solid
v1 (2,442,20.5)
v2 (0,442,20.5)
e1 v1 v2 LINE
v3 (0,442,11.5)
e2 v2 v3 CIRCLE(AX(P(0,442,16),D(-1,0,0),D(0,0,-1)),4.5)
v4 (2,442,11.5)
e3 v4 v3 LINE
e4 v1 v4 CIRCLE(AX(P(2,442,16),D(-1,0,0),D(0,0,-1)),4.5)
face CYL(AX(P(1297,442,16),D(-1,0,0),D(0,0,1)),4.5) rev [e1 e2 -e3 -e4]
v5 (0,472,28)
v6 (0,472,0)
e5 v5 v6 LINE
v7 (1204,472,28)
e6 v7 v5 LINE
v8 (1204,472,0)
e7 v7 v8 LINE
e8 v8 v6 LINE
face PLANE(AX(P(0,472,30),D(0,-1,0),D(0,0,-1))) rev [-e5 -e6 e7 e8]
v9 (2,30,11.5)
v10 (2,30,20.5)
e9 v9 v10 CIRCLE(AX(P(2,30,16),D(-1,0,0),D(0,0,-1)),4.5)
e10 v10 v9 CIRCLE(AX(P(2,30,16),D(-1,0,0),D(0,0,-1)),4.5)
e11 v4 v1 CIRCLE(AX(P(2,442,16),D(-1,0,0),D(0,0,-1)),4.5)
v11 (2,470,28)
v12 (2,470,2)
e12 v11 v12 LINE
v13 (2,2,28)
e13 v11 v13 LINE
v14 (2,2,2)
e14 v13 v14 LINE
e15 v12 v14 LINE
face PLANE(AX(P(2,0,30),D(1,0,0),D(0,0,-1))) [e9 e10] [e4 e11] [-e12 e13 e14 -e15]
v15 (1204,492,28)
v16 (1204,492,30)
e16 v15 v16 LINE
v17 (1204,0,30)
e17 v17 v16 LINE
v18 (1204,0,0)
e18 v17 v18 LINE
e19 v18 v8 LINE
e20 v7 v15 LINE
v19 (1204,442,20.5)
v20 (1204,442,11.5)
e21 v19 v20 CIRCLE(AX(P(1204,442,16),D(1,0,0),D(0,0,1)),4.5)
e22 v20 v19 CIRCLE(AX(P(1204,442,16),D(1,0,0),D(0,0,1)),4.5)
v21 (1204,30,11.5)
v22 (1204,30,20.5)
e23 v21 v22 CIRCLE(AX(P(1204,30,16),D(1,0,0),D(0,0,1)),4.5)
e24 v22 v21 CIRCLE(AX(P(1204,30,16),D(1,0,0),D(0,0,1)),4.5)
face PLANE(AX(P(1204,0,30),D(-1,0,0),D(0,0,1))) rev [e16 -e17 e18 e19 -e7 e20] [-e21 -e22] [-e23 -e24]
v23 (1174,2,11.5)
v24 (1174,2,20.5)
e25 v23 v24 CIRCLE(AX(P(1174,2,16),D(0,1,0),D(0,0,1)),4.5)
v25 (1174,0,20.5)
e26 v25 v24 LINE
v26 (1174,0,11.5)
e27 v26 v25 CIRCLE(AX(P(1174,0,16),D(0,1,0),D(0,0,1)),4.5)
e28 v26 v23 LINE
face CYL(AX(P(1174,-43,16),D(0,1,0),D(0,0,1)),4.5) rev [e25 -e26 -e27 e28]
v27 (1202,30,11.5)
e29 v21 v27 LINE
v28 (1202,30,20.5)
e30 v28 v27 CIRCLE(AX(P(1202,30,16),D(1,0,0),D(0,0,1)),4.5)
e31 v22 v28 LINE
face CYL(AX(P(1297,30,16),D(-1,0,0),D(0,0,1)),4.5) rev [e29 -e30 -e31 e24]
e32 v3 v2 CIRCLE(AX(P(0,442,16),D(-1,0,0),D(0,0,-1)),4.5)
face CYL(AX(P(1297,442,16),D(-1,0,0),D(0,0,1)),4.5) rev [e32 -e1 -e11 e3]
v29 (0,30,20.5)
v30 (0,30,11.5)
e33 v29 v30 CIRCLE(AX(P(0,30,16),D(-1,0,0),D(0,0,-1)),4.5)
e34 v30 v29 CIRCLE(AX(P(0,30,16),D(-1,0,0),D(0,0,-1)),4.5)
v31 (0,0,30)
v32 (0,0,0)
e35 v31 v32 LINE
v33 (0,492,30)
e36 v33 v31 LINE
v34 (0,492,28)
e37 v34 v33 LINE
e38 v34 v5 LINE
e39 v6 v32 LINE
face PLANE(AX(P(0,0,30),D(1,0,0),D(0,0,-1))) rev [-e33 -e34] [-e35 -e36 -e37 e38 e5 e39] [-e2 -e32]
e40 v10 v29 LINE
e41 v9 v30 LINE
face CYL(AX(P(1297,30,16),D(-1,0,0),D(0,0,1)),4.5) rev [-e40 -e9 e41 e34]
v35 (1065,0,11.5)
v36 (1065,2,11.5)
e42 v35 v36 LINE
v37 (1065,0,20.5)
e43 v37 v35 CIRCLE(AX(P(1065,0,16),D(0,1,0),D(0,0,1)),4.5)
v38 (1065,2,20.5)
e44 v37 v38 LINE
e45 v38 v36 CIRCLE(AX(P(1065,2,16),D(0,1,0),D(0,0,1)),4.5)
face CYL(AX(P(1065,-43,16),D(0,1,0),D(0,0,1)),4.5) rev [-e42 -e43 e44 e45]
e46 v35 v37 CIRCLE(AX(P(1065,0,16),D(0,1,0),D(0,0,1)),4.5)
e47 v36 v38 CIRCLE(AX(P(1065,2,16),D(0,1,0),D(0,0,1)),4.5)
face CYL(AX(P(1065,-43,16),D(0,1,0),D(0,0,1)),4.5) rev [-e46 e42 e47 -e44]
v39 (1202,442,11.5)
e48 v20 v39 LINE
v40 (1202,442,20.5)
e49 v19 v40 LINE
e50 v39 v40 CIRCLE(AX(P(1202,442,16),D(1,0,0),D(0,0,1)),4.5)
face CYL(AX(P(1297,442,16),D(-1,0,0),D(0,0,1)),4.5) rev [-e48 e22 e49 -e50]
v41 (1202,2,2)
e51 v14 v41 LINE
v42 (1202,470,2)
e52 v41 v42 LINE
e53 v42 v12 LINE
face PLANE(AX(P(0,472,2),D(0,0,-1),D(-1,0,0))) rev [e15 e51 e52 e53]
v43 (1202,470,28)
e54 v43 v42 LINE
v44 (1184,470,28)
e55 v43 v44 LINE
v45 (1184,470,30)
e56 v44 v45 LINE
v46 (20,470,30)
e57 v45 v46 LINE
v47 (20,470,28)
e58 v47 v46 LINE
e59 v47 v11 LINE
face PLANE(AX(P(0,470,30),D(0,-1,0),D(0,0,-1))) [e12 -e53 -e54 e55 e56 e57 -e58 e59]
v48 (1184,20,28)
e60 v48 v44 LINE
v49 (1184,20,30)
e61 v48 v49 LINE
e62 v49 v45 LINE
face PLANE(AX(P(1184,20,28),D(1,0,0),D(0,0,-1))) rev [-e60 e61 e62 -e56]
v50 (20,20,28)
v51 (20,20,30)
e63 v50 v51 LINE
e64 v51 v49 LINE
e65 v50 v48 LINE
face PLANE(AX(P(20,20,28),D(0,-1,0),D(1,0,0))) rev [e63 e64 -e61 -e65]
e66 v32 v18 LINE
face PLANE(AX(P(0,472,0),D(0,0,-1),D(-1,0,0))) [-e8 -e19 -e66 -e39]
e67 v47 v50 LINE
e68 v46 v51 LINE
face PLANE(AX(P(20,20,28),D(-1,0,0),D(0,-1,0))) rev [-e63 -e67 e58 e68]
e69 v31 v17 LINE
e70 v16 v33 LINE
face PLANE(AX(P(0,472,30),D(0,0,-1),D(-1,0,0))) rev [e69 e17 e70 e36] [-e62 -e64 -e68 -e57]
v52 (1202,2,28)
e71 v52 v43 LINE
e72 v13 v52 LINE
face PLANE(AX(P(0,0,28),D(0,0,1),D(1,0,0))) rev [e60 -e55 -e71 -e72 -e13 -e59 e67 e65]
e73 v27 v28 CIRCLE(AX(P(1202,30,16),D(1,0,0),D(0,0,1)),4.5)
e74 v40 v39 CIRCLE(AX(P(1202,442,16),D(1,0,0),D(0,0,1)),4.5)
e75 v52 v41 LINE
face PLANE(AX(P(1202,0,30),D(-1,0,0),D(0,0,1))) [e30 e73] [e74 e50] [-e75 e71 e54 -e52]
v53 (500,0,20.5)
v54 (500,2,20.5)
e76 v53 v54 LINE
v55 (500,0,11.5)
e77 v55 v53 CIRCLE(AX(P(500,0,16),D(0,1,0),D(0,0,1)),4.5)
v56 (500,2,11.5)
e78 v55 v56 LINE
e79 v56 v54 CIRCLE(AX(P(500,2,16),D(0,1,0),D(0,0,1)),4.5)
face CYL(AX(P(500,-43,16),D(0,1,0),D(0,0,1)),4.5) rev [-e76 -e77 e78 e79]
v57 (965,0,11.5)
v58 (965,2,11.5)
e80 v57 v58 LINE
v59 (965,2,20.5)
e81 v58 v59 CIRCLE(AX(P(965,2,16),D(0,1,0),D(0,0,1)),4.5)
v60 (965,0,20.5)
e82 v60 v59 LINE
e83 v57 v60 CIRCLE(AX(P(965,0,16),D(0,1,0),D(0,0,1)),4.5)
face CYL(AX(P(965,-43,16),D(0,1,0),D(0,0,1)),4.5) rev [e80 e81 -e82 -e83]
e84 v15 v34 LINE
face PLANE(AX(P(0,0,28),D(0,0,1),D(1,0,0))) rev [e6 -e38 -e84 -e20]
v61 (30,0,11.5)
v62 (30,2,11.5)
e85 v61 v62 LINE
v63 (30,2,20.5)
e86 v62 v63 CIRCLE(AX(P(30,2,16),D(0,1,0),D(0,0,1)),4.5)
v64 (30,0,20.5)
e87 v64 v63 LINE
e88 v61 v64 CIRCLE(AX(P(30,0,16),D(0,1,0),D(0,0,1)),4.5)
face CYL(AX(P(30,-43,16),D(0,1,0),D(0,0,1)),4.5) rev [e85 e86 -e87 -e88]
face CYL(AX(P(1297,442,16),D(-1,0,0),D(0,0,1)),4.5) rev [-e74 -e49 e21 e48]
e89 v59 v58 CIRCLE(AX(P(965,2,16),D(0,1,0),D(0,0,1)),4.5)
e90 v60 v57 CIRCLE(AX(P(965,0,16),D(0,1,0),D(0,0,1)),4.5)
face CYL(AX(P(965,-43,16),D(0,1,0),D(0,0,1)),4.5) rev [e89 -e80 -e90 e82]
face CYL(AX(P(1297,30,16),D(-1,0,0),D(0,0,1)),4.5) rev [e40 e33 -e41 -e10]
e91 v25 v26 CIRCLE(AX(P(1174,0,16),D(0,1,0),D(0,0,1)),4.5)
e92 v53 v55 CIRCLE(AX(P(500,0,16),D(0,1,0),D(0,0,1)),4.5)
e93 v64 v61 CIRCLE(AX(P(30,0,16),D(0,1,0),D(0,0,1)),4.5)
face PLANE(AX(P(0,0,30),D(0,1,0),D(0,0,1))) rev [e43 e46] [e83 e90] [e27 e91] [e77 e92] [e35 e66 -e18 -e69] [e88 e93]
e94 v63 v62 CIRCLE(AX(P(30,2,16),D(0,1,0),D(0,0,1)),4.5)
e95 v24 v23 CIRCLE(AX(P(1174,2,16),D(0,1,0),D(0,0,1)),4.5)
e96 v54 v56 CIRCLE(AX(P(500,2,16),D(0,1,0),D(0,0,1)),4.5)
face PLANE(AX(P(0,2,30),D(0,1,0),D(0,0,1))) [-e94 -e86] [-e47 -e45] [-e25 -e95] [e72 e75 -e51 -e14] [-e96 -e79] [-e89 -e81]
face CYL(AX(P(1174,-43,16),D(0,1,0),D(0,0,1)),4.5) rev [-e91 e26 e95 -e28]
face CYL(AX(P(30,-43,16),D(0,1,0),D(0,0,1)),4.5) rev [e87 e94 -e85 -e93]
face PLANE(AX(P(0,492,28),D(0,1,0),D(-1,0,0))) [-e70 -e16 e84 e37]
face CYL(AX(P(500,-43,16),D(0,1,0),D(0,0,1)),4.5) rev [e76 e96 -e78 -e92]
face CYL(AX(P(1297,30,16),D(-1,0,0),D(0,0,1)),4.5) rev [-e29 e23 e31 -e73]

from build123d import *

# Parameters (mm, degrees)
SKETCH_1_W               = 1204
SKETCH_1_H               = 472
EXTRUDE_1_DEPTH          = 30
SHELL_1_T                = -2
SKETCH_2_W               = 1204
SKETCH_2_H               = 492
SKETCH_2_W_2             = 1164
SKETCH_2_H_2             = 450
EXTRUDE_2_DEPTH          = 2
CUT_EXTRUDE_1_DEPTH      = 1295
CUT_EXTRUDE_1_DEPTH_BACK = 72
SKETCH_3_R               = 4.5
SKETCH_4_R               = 4.5
CUT_EXTRUDE_2_DEPTH      = 45


with BuildPart() as part:
    # 草图1 → 凸台-拉伸1 (new body)
    with BuildSketch(Plane.XY):
        with Locations((602, 236)):
            Rectangle(SKETCH_1_W, SKETCH_1_H)
    extrude(amount=EXTRUDE_1_DEPTH)

    # 抽壳1
    shell_1_openings = [part.faces().sort_by_distance(p)[0] for p in [
        (602, 236, 30),
    ]]
    offset(amount=SHELL_1_T, openings=shell_1_openings, kind=Kind.INTERSECTION)

    # 草图2 → 凸台-拉伸2 (add)
    with BuildSketch(Plane.XY.offset(30)):
        with Locations((602, 246)):
            Rectangle(SKETCH_2_W, SKETCH_2_H)
        with Locations((602, 245)):
            Rectangle(SKETCH_2_W_2, SKETCH_2_H_2, mode=Mode.SUBTRACT)
    extrude(amount=-EXTRUDE_2_DEPTH)

    # 草图3 → 切除-拉伸1 (cut, two sides: drawn at the far end of the back side and taken through both)
    with BuildSketch(Plane(origin=(2, 0, 0), x_dir=(0, 0, -1), z_dir=(1, 0, 0)).offset(-CUT_EXTRUDE_1_DEPTH_BACK)):
        with Locations(Location((-16, 442, 0), (0, 0, 180))):
            Circle(SKETCH_3_R)
        with Locations(Location((-16, 30, 0), (0, 0, 180))):
            Circle(SKETCH_3_R)
    extrude(amount=CUT_EXTRUDE_1_DEPTH + CUT_EXTRUDE_1_DEPTH_BACK, mode=Mode.SUBTRACT)

    # 草图4 → 切除-拉伸2 (cut)
    with BuildSketch(Plane(origin=(0, 2, 0), x_dir=(1, 0, 0), z_dir=(0, 1, 0))):
        with Locations(Location((1174, -16, 0), (0, 0, 270))):
            Circle(SKETCH_4_R)
        with Locations(Location((30, -16, 0), (0, 0, 270))):
            Circle(SKETCH_4_R)
        with Locations(Location((1065, -16, 0), (0, 0, 270))):
            Circle(SKETCH_4_R)
        with Locations(Location((965, -16, 0), (0, 0, 270))):
            Circle(SKETCH_4_R)
        with Locations(Location((500, -16, 0), (0, 0, 270))):
            Circle(SKETCH_4_R)
    extrude(amount=-CUT_EXTRUDE_2_DEPTH, mode=Mode.SUBTRACT)


solid = part.part
